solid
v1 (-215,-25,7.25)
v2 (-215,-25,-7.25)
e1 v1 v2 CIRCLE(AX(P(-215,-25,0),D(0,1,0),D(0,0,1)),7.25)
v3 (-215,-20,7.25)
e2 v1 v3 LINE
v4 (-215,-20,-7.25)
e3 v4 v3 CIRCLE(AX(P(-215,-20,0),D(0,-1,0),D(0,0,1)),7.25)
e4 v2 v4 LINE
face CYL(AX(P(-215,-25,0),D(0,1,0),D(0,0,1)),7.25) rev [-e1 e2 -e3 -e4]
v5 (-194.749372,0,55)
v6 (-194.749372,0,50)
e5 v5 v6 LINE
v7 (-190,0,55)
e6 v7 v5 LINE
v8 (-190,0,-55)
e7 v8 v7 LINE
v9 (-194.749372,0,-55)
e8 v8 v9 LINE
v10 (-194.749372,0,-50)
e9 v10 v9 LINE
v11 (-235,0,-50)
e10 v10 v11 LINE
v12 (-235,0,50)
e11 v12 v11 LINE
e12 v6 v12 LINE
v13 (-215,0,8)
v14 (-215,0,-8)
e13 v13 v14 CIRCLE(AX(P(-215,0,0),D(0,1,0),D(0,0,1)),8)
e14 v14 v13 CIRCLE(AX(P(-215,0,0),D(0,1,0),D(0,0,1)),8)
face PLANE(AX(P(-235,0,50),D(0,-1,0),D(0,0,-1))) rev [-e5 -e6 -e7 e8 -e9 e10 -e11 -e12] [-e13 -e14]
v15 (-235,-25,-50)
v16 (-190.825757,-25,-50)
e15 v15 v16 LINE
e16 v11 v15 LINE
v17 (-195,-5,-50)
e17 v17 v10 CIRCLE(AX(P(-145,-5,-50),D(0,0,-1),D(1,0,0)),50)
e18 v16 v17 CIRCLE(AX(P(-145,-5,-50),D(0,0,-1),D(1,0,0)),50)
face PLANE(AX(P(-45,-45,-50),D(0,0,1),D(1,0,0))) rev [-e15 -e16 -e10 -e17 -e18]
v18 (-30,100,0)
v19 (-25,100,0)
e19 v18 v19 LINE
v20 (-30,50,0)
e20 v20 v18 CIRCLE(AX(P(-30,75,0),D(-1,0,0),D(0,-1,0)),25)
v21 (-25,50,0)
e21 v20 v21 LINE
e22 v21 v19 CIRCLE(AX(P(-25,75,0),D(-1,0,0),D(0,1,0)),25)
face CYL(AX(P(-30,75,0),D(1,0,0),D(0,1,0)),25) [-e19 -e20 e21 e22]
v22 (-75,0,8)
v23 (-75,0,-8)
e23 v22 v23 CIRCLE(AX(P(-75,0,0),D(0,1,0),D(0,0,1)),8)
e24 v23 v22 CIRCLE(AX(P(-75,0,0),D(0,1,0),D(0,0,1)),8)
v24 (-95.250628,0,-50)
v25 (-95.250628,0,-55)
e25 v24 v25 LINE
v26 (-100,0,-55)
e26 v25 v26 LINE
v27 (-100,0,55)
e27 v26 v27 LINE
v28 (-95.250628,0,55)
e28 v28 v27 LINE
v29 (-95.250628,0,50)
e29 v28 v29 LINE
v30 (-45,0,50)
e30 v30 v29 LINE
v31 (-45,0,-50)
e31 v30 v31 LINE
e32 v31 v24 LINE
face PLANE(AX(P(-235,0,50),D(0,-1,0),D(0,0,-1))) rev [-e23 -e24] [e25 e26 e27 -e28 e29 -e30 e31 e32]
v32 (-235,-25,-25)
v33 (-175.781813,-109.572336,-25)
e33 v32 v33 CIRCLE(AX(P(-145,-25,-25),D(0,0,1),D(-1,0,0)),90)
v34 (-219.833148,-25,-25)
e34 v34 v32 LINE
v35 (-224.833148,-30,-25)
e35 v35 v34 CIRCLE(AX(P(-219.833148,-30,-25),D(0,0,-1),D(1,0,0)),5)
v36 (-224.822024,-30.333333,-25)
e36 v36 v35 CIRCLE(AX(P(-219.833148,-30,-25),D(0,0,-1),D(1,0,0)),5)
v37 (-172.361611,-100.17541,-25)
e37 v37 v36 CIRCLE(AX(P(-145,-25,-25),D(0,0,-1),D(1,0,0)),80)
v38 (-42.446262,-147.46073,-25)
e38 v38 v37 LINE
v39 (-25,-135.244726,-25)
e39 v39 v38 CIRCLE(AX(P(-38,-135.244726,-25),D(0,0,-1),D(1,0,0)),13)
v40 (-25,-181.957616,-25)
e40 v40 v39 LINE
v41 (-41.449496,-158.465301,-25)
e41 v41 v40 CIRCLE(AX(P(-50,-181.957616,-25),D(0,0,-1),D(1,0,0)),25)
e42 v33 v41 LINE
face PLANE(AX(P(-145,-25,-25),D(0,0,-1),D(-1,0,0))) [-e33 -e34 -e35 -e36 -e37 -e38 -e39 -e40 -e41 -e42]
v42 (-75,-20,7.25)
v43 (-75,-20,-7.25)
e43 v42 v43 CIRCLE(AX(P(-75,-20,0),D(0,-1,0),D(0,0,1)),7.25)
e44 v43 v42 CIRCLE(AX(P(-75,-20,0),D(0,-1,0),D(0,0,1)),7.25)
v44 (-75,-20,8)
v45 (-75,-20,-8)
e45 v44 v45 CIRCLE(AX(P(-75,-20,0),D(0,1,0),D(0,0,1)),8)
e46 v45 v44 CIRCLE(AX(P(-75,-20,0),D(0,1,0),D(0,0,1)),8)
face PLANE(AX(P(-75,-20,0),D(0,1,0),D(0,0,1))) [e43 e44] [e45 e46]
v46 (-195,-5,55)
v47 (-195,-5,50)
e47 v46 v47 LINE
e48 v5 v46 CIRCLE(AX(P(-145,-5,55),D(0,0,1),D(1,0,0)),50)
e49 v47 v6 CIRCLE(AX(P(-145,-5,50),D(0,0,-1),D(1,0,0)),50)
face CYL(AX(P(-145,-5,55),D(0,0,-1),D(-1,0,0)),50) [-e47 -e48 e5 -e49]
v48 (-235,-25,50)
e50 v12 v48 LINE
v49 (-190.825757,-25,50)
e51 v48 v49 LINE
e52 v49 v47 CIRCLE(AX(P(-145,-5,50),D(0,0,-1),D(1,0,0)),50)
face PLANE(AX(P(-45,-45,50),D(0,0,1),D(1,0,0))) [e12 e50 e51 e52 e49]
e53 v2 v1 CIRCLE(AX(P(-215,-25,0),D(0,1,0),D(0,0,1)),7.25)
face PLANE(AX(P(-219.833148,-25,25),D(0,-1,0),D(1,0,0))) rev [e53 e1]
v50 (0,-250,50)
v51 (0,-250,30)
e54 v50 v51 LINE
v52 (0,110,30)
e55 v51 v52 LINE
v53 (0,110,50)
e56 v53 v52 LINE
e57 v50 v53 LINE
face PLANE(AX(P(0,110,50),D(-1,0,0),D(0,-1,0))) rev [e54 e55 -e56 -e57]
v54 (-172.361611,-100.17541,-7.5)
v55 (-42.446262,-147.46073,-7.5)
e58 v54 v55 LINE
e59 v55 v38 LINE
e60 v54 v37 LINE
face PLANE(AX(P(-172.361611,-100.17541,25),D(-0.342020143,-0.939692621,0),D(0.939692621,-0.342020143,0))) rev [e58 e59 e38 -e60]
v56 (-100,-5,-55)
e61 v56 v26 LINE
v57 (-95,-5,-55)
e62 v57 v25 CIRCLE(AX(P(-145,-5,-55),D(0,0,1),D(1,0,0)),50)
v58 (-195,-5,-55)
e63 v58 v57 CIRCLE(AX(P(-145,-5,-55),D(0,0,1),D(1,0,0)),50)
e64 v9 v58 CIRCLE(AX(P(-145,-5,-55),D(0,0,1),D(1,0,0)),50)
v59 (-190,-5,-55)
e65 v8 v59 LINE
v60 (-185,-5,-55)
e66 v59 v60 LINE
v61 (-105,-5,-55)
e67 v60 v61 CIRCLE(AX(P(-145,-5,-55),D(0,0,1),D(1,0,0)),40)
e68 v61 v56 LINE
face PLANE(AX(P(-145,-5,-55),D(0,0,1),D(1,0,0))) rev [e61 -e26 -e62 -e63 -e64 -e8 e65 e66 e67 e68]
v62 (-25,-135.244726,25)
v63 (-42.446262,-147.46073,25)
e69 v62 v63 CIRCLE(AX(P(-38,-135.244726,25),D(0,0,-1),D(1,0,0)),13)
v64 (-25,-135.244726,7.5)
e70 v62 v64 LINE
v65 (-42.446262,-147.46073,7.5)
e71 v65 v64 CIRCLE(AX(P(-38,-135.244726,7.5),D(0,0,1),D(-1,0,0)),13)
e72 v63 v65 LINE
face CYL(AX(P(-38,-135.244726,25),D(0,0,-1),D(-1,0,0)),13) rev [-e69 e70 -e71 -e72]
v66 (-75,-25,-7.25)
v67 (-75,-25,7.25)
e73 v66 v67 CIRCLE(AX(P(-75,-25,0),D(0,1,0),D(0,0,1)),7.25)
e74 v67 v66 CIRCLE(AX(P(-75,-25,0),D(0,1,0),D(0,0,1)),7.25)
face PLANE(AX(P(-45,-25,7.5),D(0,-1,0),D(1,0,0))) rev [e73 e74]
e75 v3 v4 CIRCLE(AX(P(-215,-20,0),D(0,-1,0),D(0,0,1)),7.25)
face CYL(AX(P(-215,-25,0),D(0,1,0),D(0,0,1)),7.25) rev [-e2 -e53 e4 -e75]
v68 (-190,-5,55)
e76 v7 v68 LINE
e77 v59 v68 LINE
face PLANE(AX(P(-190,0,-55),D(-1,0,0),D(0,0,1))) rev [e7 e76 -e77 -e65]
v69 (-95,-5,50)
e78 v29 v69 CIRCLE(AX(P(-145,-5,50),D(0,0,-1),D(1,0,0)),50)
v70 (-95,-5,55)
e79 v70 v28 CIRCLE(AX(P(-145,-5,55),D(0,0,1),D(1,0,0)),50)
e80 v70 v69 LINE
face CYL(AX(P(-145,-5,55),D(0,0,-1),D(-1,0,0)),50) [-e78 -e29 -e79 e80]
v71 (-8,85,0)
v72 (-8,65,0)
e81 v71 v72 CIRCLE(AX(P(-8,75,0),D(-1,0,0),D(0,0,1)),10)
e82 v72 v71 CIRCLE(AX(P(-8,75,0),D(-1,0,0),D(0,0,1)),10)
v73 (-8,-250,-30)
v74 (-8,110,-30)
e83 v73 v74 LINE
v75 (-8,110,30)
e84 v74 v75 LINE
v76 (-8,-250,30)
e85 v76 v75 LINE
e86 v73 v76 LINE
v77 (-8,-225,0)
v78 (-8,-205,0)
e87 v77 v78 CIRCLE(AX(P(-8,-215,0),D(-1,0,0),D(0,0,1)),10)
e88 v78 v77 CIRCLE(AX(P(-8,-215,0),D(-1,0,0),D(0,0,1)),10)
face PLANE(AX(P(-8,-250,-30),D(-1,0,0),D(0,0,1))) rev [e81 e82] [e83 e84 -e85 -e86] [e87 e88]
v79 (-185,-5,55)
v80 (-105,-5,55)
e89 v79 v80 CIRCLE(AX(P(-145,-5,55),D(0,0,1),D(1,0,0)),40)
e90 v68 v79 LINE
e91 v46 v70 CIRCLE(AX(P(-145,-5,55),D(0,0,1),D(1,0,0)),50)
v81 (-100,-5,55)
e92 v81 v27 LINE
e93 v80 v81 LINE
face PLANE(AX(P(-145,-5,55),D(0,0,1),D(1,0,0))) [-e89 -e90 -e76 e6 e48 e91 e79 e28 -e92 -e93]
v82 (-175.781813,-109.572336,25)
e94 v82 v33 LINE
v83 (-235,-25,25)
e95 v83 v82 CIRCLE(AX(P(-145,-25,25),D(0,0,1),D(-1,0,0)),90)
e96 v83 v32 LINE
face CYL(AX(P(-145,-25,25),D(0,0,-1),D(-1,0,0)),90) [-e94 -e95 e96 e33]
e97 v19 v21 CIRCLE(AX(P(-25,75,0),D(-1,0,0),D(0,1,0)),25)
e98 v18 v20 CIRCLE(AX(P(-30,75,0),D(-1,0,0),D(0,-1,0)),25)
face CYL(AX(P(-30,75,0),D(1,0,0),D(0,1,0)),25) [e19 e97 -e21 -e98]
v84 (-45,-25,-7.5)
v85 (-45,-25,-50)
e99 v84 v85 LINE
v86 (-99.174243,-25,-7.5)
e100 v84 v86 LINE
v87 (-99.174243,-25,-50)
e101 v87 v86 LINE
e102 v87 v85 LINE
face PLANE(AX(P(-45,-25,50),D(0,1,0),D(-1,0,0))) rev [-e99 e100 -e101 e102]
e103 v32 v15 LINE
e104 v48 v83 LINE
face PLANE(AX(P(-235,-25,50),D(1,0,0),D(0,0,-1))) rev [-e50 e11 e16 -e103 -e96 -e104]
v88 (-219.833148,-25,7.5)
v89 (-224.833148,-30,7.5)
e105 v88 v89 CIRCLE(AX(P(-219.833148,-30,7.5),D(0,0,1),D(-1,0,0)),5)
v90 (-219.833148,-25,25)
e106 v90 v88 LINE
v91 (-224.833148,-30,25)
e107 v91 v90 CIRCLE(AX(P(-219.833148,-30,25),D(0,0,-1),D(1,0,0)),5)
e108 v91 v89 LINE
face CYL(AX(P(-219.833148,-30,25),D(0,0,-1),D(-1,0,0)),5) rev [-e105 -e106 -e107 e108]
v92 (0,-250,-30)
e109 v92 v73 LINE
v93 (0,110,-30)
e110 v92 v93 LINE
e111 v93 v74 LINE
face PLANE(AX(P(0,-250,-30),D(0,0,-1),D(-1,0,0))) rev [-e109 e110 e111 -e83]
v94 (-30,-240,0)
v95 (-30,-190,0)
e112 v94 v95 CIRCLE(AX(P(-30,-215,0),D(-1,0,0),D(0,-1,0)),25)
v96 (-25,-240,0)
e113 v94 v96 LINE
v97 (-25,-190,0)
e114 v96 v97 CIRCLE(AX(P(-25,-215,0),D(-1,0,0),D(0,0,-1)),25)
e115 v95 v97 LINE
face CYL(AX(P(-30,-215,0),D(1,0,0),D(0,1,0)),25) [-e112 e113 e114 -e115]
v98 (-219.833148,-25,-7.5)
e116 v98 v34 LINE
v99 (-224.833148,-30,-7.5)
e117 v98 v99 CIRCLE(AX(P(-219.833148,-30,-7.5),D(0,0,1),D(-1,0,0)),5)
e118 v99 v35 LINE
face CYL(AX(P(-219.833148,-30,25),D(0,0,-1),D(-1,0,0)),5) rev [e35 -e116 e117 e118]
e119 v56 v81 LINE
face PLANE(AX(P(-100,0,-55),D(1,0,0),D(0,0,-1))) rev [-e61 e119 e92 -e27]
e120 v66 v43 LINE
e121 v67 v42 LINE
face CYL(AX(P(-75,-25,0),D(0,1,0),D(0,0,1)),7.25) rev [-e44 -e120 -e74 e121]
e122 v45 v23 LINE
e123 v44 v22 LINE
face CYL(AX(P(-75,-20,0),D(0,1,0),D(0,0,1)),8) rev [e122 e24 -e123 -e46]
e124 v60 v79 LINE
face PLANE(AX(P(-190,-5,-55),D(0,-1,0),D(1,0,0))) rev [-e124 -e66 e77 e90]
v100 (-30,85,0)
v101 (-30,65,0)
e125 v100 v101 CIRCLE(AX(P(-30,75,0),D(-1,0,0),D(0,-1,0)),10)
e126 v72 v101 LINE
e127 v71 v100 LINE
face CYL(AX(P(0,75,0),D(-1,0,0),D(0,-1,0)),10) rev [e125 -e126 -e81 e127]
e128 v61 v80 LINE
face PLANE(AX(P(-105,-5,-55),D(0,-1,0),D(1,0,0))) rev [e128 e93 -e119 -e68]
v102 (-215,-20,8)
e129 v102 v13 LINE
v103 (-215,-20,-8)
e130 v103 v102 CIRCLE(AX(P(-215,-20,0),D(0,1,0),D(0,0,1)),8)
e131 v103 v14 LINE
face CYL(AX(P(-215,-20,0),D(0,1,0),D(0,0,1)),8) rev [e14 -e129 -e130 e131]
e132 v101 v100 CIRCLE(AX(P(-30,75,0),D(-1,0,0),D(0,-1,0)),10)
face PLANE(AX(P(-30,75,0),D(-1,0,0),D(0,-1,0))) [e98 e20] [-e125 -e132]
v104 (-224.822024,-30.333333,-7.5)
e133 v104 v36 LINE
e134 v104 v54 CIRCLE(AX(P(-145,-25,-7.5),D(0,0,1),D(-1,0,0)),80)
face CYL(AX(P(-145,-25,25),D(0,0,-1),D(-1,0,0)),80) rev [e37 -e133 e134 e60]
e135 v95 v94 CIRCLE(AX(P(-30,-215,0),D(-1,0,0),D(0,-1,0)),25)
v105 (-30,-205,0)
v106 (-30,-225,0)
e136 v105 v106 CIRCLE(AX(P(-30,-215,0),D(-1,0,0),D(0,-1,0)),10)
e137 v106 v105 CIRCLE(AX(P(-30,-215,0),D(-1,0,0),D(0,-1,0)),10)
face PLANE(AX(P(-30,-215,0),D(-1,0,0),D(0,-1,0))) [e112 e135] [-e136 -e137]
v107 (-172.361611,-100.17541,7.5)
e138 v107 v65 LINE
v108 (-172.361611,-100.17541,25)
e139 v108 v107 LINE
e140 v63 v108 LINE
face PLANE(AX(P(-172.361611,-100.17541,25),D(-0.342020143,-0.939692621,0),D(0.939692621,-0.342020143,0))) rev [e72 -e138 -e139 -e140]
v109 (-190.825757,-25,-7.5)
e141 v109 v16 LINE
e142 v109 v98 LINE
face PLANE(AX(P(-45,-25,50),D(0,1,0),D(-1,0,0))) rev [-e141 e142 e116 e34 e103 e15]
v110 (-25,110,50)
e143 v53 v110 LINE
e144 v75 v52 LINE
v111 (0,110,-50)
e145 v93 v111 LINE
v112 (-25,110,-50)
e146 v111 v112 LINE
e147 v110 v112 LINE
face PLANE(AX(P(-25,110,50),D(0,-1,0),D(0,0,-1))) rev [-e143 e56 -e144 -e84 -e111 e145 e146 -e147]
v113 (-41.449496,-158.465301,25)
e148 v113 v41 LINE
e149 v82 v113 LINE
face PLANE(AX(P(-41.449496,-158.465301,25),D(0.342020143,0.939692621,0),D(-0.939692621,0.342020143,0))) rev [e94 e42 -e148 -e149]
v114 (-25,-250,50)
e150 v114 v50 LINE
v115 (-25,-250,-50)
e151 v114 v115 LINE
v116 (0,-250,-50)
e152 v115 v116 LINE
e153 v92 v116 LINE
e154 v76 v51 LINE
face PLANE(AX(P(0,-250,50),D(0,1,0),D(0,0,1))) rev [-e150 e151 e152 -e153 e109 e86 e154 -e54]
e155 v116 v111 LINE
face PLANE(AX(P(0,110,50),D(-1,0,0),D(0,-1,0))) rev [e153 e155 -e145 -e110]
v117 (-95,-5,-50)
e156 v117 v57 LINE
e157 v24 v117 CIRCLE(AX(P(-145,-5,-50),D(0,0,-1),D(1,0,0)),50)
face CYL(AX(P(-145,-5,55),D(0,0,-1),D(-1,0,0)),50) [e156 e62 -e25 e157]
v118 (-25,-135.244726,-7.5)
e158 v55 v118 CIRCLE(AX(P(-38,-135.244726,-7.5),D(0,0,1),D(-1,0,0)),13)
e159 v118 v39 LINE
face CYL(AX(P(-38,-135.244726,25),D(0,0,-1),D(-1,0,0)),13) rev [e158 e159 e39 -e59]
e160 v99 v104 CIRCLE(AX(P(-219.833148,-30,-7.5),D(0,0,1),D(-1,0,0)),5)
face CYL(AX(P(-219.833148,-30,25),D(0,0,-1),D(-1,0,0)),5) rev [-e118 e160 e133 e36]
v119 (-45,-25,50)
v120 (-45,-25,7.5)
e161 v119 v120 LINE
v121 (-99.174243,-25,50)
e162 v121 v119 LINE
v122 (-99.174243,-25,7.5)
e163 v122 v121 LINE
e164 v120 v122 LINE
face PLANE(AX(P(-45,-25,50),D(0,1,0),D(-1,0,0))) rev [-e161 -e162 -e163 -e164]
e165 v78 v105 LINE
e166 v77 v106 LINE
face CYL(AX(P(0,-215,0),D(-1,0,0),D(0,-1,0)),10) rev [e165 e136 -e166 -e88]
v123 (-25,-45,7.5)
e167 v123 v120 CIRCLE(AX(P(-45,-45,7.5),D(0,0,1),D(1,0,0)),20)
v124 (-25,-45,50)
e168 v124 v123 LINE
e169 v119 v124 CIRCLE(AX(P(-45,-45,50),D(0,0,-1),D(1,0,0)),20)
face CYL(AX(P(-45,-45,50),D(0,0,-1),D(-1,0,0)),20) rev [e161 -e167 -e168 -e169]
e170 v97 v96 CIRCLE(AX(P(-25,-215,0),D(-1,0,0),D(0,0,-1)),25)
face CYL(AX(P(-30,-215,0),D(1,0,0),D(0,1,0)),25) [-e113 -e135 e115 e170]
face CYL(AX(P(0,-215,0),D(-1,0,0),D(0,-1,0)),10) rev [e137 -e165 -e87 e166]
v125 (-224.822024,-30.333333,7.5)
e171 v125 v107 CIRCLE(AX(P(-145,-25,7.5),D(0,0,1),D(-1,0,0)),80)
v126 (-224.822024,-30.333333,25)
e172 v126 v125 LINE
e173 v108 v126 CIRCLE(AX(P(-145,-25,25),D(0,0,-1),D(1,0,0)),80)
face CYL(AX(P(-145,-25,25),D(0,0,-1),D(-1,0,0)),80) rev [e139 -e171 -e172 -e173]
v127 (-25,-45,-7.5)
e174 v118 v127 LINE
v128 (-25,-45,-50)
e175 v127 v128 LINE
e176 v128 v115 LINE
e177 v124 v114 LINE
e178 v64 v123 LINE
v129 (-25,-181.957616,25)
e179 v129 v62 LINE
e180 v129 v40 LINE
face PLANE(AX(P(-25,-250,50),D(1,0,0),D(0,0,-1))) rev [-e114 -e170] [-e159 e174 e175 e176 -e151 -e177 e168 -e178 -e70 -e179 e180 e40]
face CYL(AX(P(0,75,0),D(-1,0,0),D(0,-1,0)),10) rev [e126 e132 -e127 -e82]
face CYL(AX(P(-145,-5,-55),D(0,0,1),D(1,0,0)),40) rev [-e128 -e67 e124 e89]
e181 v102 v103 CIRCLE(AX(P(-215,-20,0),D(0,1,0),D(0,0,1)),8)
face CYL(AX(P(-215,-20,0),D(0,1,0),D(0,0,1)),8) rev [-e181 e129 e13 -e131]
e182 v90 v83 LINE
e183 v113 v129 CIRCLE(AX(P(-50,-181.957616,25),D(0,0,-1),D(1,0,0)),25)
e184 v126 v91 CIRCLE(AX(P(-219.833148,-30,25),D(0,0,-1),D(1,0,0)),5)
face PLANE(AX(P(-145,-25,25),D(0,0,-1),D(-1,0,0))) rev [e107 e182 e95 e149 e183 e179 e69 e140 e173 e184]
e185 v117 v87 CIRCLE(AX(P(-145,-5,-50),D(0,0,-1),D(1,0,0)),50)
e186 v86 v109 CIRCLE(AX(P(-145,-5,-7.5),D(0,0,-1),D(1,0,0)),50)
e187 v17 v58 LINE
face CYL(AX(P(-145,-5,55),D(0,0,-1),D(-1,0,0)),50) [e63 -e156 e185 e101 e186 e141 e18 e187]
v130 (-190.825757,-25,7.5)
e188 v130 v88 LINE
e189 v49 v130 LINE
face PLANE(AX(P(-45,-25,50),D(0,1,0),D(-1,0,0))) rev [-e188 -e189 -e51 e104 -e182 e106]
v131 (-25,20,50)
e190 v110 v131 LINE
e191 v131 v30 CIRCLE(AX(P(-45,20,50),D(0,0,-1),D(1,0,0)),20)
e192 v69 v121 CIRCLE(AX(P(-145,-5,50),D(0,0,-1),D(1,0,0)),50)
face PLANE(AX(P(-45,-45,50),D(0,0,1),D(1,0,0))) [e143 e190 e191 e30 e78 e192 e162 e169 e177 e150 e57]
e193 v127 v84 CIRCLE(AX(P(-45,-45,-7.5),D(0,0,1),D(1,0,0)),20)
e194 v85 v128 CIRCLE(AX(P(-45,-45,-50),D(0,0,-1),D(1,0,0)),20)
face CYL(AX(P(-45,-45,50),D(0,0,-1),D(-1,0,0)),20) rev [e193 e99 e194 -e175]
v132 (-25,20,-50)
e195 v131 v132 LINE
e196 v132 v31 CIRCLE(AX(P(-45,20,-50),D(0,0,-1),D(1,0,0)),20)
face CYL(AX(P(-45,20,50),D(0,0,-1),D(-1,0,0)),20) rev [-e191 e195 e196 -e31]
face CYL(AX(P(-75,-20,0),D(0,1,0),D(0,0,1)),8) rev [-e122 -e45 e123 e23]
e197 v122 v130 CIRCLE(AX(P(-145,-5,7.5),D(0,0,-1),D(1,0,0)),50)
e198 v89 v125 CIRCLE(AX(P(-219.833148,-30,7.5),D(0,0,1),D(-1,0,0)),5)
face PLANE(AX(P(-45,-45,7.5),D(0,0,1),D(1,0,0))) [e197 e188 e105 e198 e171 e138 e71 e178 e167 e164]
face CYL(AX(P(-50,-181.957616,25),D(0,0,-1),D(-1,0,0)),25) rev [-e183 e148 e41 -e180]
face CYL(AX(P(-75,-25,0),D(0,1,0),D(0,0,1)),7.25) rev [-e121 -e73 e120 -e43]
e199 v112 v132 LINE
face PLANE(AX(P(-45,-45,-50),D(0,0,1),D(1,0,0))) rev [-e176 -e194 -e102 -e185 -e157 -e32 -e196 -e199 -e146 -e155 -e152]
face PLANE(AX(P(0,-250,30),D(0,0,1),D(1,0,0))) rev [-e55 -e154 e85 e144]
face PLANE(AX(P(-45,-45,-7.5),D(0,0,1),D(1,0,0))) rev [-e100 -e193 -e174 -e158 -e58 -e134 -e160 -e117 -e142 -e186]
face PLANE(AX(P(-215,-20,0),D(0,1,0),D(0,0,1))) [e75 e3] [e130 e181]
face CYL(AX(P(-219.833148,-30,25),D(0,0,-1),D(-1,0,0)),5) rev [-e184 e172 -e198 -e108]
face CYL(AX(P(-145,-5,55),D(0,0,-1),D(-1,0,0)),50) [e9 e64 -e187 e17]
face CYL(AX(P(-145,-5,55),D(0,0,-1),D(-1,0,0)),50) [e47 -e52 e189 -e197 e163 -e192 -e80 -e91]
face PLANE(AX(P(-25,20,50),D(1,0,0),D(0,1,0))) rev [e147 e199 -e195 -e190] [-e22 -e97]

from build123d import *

# Parameters (mm, degrees)
BRACKET_BODY_DEPTH     = 50
POCKET_SKETCH_W        = 8
POCKET_SKETCH_H        = 60
POCKET_60X30_DEPTH     = 433.810582126
RAISED_PAD_SKETCH_R    = 25
RAISED_PAD_5MM_DEPTH   = 5
PAD_HOLE_SKETCH_R      = 10
PAD_HOLES_DEPTH        = 328.146756059
MOUNTING_HOLE_SKETCH_R = 7.25
MOUNTING_HOLES_DEPTH   = 25
THROUGH_HOLE_SKETCH_R  = 8
THROUGH_HOLES_16_DEPTH = 20
SADDLE_BLOCK_DEPTH     = 55
PIPE_SADDLE_CUT_DEPTH  = 55
SUPPORT_ARM_DEPTH      = 25
SUPPORT_WEB_15MM_DEPTH = 7.5


with BuildPart() as part:
    # Bracket Profile Sketch → Bracket Body (new, symmetric)
    with BuildSketch(Plane.XY):
        with BuildLine():
            Line((0, 110), (0, -250))
            Line((0, -250), (-25, -250))
            Line((-25, -250), (-25, -45))
            ThreePointArc((-25, -45), (-30.857864376, -30.857864376), (-45, -25))
            Line((-45, -25), (-235, -25))
            Line((-235, -25), (-235, 0))
            Line((-235, 0), (-45, 0))
            ThreePointArc((-45, 0), (-30.857864376, 5.857864376), (-25, 20))
            Line((-25, 20), (-25, 110))
            Line((-25, 110), (0, 110))
        make_face()
    extrude(amount=BRACKET_BODY_DEPTH, both=True)

    # Pocket Sketch → Pocket 60x30 (cut, through all)
    with BuildSketch(Plane(origin=(0, 110, 0), x_dir=(1, 0, 0), z_dir=(0, 1, 0))):
        with Locations((-4, 0)):
            Rectangle(POCKET_SKETCH_W, POCKET_SKETCH_H)
    extrude(amount=-POCKET_60X30_DEPTH, mode=Mode.SUBTRACT)

    # Raised Pad Sketch → Raised Pad 5mm (add)
    with BuildSketch(Plane.ZY.offset(25)):
        with Locations(Location((0, 75, 0), (0, 0, 90))):
            Circle(RAISED_PAD_SKETCH_R)
        with Locations(Location((0, -215, 0), (0, 0, 180))):
            Circle(RAISED_PAD_SKETCH_R)
    extrude(amount=RAISED_PAD_5MM_DEPTH)

    # Pad Hole Sketch → Pad Holes (cut, through all)
    with BuildSketch(Plane.ZY.offset(30)):
        with Locations(Location((0, 75, 0), (0, 0, 270))):
            Circle(PAD_HOLE_SKETCH_R)
        with Locations(Location((0, -215, 0), (0, 0, 270))):
            Circle(PAD_HOLE_SKETCH_R)
    extrude(amount=-PAD_HOLES_DEPTH, mode=Mode.SUBTRACT)

    # Mounting Hole Sketch → Mounting Holes (cut)
    with BuildSketch(Plane(origin=(0, 0, 0), x_dir=(1, 0, 0), z_dir=(0, 1, 0))):
        with Locations(Location((-75, 0, 0), (0, 0, 270))):
            Circle(MOUNTING_HOLE_SKETCH_R)
        with Locations(Location((-215, 0, 0), (0, 0, 270))):
            Circle(MOUNTING_HOLE_SKETCH_R)
    extrude(amount=-MOUNTING_HOLES_DEPTH, mode=Mode.SUBTRACT)

    # Through Hole Sketch → Through Holes Ø16 (cut)
    with BuildSketch(Plane(origin=(0, 0, 0), x_dir=(1, 0, 0), z_dir=(0, 1, 0))):
        with Locations(Location((-75, 0, 0), (0, 0, 270))):
            Circle(THROUGH_HOLE_SKETCH_R)
        with Locations(Location((-215, 0, 0), (0, 0, 270))):
            Circle(THROUGH_HOLE_SKETCH_R)
    extrude(amount=-THROUGH_HOLES_16_DEPTH, mode=Mode.SUBTRACT)

    # Saddle Block Sketch → Saddle Block (add, symmetric)
    with BuildSketch(Plane.XY):
        with BuildLine():
            Line((-194.749371855, 0), (-95.250628145, 0))
            ThreePointArc((-95.250628145, 0), (-145, -55), (-194.749371855, 0))
        make_face()
    extrude(amount=SADDLE_BLOCK_DEPTH, both=True)

    # Pipe Saddle Cut Sketch → Pipe Saddle Cut (cut, symmetric)
    with BuildSketch(Plane.XY):
        with BuildLine():
            Line((-190, 0), (-100, 0))
            Line((-100, 0), (-100, -5))
            Line((-100, -5), (-105, -5))
            ThreePointArc((-105, -5), (-145, -45), (-185, -5))
            Line((-185, -5), (-190, -5))
            Line((-190, -5), (-190, 0))
        make_face()
    extrude(amount=PIPE_SADDLE_CUT_DEPTH, both=True, mode=Mode.SUBTRACT)

    # Support Arm Sketch → Support Arm (add, symmetric)
    with BuildSketch(Plane.XY):
        with BuildLine():
            Line((-41.449496417, -158.46530057), (-175.781812899, -109.572335871))
            ThreePointArc((-175.781812899, -109.572335871), (-218.723683986, -76.621879272), (-235, -25))
            Line((-235, -25), (-219.833147735, -25))
            ThreePointArc((-219.833147735, -25), (-223.484631452, -26.584349745), (-224.822024251, -30.333333333))
            ThreePointArc((-224.822024251, -30.333333333), (-208.965317539, -73.046208509), (-172.361611466, -100.175409663))
            Line((-172.361611466, -100.175409663), (-42.446261863, -147.460729893))
            ThreePointArc((-42.446261863, -147.460729893), (-30.543506327, -145.893702398), (-25, -135.244725822))
            Line((-25, -135.244725822), (-25, -181.95761609))
            ThreePointArc((-25, -181.95761609), (-29.521198893, -167.618205181), (-41.449496417, -158.46530057))
        make_face()
    extrude(amount=SUPPORT_ARM_DEPTH, both=True)

    # Support Web Sketch → Support Web 15mm (add, symmetric)
    with BuildSketch(Plane.XY):
        with BuildLine():
            Line((-25, -45), (-25, -135.244725822))
            ThreePointArc((-25, -135.244725822), (-30.543506327, -145.893702398), (-42.446261863, -147.460729893))
            Line((-42.446261863, -147.460729893), (-172.361611466, -100.175409663))
            ThreePointArc((-172.361611466, -100.175409663), (-208.965317539, -73.046208509), (-224.822024251, -30.333333333))
            ThreePointArc((-224.822024251, -30.333333333), (-223.484631452, -26.584349745), (-219.833147735, -25))
            Line((-219.833147735, -25), (-190.82575695, -25))
            ThreePointArc((-190.82575695, -25), (-145, -55), (-99.17424305, -25))
            Line((-99.17424305, -25), (-45, -25))
            ThreePointArc((-45, -25), (-30.857864376, -30.857864376), (-25, -45))
        make_face()
    extrude(amount=SUPPORT_WEB_15MM_DEPTH, both=True)


solid = part.part
